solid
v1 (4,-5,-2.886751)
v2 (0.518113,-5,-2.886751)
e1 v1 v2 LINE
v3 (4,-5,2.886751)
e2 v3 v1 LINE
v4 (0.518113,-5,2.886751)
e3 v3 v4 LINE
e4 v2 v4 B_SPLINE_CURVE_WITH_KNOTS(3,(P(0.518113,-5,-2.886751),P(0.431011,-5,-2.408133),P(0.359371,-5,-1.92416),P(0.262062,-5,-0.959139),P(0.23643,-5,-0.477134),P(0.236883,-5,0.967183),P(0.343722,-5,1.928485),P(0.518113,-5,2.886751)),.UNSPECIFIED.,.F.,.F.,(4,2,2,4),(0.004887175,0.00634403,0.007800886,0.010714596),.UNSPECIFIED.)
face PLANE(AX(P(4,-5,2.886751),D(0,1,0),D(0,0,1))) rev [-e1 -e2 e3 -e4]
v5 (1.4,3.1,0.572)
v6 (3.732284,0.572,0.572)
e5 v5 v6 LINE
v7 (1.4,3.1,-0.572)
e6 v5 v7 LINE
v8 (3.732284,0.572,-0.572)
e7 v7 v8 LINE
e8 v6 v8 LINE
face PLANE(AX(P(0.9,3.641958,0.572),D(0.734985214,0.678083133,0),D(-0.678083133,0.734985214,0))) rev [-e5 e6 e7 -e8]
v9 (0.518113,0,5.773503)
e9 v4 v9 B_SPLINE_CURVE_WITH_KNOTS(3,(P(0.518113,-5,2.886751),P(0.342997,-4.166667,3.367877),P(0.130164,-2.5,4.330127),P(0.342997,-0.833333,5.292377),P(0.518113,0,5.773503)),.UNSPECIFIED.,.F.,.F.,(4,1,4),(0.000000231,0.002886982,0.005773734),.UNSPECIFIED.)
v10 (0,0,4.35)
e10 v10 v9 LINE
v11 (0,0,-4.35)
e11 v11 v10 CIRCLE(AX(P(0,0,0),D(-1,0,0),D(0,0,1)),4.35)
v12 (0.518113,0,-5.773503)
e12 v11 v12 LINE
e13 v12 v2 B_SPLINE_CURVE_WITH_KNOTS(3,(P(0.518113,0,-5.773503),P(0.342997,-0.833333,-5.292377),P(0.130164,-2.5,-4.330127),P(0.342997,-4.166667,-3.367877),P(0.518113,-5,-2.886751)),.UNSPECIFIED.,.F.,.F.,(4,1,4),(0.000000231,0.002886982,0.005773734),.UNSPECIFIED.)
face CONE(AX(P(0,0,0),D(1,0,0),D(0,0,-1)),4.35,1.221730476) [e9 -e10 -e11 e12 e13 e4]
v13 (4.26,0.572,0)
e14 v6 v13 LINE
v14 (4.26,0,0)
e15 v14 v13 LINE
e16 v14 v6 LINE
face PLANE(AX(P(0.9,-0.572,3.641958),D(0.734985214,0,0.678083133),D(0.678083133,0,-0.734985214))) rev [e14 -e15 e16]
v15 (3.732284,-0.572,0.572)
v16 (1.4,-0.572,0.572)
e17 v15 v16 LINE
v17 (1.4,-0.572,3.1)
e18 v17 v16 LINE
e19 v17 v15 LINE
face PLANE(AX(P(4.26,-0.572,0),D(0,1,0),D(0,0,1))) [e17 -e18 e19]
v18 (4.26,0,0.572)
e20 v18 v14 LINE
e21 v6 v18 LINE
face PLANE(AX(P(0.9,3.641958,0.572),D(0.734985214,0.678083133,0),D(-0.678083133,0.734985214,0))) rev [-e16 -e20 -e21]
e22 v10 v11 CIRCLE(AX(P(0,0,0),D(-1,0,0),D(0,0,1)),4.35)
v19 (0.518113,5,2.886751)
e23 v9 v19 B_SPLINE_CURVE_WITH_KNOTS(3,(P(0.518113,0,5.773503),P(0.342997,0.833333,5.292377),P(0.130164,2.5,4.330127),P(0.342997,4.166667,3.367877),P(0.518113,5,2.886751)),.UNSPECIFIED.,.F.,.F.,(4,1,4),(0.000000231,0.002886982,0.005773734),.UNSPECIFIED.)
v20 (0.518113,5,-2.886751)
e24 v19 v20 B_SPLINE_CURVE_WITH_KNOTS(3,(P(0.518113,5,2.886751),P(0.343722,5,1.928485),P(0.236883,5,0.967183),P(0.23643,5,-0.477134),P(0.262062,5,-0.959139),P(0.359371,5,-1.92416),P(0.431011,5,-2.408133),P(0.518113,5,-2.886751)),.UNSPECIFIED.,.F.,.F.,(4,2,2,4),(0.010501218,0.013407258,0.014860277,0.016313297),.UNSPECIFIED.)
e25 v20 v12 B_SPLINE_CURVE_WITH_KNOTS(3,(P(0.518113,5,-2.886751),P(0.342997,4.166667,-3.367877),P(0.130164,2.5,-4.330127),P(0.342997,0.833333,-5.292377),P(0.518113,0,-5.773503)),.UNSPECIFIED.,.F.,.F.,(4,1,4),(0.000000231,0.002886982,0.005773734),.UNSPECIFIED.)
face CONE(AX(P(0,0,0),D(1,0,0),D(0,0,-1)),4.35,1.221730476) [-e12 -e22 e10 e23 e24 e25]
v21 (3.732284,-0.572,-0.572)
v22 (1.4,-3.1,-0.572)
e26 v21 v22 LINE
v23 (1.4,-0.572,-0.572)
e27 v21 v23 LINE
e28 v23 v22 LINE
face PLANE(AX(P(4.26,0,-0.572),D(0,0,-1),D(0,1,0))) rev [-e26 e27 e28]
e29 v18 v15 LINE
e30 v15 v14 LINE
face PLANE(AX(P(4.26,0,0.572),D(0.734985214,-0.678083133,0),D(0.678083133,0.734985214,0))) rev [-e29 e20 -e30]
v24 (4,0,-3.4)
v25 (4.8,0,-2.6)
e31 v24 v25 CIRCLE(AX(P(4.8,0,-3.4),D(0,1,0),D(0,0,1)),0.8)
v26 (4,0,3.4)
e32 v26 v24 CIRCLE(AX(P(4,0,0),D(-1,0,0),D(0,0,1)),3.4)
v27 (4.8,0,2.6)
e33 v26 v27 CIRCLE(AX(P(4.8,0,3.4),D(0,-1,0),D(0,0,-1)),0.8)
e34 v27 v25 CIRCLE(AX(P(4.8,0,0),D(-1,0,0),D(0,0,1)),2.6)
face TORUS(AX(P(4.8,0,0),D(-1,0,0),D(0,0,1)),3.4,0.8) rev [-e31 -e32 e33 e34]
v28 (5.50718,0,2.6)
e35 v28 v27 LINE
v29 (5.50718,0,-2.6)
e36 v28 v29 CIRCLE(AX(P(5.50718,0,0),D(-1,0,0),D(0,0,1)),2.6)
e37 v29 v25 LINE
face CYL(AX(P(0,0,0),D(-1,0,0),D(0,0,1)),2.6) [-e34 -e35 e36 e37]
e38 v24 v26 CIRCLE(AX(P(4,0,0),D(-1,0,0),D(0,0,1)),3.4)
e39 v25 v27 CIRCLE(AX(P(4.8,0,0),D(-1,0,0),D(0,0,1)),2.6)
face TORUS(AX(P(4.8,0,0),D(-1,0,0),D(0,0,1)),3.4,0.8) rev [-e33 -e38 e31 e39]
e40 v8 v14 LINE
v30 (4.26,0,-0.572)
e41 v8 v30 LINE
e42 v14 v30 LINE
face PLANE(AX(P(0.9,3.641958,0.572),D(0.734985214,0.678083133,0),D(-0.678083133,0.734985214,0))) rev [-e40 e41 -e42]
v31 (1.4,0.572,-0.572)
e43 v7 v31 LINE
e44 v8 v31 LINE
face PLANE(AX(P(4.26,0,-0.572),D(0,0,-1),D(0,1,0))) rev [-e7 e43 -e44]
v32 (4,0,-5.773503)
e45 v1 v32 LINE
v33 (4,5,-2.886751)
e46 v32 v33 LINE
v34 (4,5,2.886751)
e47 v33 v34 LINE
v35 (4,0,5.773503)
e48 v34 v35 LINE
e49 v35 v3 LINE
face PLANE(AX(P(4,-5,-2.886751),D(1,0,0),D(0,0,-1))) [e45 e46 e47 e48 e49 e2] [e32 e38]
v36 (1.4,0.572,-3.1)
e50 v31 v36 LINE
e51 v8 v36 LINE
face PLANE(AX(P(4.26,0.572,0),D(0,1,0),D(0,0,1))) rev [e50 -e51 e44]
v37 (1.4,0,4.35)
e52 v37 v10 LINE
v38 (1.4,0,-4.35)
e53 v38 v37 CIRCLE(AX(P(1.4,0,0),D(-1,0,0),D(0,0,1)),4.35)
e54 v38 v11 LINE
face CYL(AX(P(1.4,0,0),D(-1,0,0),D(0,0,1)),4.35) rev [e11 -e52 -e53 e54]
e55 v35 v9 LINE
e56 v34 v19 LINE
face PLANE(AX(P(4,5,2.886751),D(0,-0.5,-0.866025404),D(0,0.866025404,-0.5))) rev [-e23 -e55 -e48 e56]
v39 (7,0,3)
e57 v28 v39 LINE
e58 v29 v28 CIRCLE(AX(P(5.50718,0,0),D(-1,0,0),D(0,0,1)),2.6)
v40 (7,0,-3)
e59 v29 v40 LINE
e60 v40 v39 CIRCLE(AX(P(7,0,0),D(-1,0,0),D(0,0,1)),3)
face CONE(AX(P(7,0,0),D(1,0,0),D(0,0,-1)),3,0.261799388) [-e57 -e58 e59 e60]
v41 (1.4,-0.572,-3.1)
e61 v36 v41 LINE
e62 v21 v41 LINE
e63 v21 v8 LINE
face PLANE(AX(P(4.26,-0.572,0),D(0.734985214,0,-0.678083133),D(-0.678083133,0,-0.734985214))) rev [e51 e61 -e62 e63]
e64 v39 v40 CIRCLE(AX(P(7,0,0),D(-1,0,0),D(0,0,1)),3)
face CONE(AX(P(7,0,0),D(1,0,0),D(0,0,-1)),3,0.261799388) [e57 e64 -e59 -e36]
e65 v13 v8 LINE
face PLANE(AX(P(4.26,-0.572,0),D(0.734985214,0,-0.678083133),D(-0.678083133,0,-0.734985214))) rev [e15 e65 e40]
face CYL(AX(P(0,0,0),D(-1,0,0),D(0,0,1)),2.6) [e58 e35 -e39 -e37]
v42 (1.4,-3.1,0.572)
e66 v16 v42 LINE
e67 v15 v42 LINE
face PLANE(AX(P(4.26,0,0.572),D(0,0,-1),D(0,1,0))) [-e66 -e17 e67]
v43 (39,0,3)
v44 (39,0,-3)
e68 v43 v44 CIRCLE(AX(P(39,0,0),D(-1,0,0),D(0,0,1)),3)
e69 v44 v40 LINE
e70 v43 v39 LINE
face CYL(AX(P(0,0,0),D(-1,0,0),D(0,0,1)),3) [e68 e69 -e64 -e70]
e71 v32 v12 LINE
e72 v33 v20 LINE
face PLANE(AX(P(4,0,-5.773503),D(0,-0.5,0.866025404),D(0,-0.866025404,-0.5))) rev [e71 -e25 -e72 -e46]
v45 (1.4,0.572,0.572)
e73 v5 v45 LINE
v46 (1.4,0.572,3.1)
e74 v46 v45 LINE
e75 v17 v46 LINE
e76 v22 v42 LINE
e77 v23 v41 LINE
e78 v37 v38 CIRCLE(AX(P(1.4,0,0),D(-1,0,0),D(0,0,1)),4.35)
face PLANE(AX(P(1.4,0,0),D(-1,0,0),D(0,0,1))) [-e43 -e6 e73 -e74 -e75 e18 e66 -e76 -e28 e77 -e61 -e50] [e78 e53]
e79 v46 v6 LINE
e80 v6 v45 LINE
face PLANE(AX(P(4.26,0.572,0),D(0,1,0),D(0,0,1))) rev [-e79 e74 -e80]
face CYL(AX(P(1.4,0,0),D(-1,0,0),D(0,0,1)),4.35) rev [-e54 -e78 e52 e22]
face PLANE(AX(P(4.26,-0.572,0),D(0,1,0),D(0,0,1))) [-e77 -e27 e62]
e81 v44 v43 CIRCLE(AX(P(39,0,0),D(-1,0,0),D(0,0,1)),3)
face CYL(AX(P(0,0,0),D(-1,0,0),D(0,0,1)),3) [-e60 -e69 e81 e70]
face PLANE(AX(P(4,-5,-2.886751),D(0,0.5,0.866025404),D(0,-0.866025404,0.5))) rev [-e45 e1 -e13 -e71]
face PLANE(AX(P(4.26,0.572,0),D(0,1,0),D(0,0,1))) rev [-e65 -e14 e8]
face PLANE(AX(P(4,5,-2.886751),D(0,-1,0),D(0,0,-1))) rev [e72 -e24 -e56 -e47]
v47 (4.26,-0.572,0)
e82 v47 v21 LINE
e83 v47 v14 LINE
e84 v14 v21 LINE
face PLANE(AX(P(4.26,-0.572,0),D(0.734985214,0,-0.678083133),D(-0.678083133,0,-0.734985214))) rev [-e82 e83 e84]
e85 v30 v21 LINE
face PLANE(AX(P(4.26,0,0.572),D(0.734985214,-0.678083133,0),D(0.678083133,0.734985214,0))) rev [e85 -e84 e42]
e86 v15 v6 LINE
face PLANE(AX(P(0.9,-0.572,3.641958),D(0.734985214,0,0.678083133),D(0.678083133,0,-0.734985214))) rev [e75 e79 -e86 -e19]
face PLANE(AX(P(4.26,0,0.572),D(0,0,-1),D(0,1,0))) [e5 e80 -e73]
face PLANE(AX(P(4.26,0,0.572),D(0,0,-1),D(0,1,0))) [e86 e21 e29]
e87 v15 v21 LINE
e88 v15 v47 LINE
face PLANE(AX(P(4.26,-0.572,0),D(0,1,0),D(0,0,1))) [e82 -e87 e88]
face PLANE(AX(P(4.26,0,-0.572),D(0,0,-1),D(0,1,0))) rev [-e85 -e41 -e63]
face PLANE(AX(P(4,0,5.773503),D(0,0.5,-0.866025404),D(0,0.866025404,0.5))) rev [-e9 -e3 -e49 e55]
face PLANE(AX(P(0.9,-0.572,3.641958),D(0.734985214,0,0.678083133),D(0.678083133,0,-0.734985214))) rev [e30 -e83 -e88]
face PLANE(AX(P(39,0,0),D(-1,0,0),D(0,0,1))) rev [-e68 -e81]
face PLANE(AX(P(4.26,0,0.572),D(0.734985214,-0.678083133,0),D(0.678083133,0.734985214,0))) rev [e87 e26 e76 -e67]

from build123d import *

# Parameters (mm, degrees)
BASEHEAD_DEPTH     = 4
SKETCH6_R          = 4.35
CUT_EXTRUDE1_DEPTH = 1.4
CUT_EXTRUDE2_DEPTH = 0.572
CIRPATTERN2_COUNT  = 2
CIRPATTERN2_ANGLE  = 90


with BuildPart() as part:
    # Sketch2 → BaseHead (new body)
    with BuildSketch(Plane(origin=(0, 0, 0), x_dir=(0, 0, -1), z_dir=(1, 0, 0))):
        Polygon((2.886751346, -5), (5.773502692, 0), (2.886751346, 5), (-2.886751346, 5), (-5.773502692, 0), (-2.886751346, -5), align=None)
    extrude(amount=BASEHEAD_DEPTH)

    # Sketch10 → Revolve1 (revolve)
    with BuildSketch(Plane(origin=(0, 0, 0), x_dir=(1, 0, 0), z_dir=(0, 1, 0)), mode=Mode.PRIVATE) as revolve1_sk:
        with BuildLine():
            Line((4, 3.4), (4, 0))
            Line((4, 0), (39, 0))
            Line((39, 0), (39, 3))
            Line((39, 3), (7, 3))
            Line((7, 3), (5.507179677, 2.6))
            Line((5.507179677, 2.6), (4.8, 2.6))
            ThreePointArc((4.8, 2.6), (4.234314575, 2.834314575), (4, 3.4))
        make_face()
    revolve(revolve1_sk.sketch.rotate(Axis((0, 0, 0), (1, 0, 0)), 180), axis=Axis((0, 0, 0), (1, 0, 0)))

    # Sketch5 → HeadChamfer (revolve, cut)
    with BuildSketch(Plane(origin=(0, 0, 0), x_dir=(1, 0, 0), z_dir=(0, 1, 0)), mode=Mode.PRIVATE) as headchamfer_sk:
        Polygon((0, 5.773502692), (0.518112608, 5.773502692), (0, 4.35), align=None)
    revolve(headchamfer_sk.sketch.rotate(Axis((-0.358389262, 0, 0), (1, 0, 0)), 180), axis=Axis((-0.358389262, 0, 0), (1, 0, 0)), mode=Mode.SUBTRACT)

    # Sketch6 → Cut-Extrude1 (cut)
    with BuildSketch(Plane.ZY):
        Circle(SKETCH6_R)
    extrude(amount=-CUT_EXTRUDE1_DEPTH, mode=Mode.SUBTRACT)

    # Sketch7 → Cut-Extrude2 (cut, symmetric)
    with BuildSketch(Plane(origin=(0, 0, 0), x_dir=(1, 0, 0), z_dir=(0, 1, 0))):
        Polygon((4.26, 0), (0.9, 3.641958042), (0.9, -3.641958042), align=None)
    cut_extrude2 = extrude(amount=CUT_EXTRUDE2_DEPTH, both=True, mode=Mode.SUBTRACT)

    # CirPattern2: Cut-Extrude2 ×2 about axis
    cirpattern2_axis = Axis((0, 0, 0), (-1, 0, 0))
    for i in range(1, CIRPATTERN2_COUNT):
        add(cut_extrude2.rotate(cirpattern2_axis, i * CIRPATTERN2_ANGLE / (CIRPATTERN2_COUNT - 1)), mode=Mode.SUBTRACT)


solid = part.part
